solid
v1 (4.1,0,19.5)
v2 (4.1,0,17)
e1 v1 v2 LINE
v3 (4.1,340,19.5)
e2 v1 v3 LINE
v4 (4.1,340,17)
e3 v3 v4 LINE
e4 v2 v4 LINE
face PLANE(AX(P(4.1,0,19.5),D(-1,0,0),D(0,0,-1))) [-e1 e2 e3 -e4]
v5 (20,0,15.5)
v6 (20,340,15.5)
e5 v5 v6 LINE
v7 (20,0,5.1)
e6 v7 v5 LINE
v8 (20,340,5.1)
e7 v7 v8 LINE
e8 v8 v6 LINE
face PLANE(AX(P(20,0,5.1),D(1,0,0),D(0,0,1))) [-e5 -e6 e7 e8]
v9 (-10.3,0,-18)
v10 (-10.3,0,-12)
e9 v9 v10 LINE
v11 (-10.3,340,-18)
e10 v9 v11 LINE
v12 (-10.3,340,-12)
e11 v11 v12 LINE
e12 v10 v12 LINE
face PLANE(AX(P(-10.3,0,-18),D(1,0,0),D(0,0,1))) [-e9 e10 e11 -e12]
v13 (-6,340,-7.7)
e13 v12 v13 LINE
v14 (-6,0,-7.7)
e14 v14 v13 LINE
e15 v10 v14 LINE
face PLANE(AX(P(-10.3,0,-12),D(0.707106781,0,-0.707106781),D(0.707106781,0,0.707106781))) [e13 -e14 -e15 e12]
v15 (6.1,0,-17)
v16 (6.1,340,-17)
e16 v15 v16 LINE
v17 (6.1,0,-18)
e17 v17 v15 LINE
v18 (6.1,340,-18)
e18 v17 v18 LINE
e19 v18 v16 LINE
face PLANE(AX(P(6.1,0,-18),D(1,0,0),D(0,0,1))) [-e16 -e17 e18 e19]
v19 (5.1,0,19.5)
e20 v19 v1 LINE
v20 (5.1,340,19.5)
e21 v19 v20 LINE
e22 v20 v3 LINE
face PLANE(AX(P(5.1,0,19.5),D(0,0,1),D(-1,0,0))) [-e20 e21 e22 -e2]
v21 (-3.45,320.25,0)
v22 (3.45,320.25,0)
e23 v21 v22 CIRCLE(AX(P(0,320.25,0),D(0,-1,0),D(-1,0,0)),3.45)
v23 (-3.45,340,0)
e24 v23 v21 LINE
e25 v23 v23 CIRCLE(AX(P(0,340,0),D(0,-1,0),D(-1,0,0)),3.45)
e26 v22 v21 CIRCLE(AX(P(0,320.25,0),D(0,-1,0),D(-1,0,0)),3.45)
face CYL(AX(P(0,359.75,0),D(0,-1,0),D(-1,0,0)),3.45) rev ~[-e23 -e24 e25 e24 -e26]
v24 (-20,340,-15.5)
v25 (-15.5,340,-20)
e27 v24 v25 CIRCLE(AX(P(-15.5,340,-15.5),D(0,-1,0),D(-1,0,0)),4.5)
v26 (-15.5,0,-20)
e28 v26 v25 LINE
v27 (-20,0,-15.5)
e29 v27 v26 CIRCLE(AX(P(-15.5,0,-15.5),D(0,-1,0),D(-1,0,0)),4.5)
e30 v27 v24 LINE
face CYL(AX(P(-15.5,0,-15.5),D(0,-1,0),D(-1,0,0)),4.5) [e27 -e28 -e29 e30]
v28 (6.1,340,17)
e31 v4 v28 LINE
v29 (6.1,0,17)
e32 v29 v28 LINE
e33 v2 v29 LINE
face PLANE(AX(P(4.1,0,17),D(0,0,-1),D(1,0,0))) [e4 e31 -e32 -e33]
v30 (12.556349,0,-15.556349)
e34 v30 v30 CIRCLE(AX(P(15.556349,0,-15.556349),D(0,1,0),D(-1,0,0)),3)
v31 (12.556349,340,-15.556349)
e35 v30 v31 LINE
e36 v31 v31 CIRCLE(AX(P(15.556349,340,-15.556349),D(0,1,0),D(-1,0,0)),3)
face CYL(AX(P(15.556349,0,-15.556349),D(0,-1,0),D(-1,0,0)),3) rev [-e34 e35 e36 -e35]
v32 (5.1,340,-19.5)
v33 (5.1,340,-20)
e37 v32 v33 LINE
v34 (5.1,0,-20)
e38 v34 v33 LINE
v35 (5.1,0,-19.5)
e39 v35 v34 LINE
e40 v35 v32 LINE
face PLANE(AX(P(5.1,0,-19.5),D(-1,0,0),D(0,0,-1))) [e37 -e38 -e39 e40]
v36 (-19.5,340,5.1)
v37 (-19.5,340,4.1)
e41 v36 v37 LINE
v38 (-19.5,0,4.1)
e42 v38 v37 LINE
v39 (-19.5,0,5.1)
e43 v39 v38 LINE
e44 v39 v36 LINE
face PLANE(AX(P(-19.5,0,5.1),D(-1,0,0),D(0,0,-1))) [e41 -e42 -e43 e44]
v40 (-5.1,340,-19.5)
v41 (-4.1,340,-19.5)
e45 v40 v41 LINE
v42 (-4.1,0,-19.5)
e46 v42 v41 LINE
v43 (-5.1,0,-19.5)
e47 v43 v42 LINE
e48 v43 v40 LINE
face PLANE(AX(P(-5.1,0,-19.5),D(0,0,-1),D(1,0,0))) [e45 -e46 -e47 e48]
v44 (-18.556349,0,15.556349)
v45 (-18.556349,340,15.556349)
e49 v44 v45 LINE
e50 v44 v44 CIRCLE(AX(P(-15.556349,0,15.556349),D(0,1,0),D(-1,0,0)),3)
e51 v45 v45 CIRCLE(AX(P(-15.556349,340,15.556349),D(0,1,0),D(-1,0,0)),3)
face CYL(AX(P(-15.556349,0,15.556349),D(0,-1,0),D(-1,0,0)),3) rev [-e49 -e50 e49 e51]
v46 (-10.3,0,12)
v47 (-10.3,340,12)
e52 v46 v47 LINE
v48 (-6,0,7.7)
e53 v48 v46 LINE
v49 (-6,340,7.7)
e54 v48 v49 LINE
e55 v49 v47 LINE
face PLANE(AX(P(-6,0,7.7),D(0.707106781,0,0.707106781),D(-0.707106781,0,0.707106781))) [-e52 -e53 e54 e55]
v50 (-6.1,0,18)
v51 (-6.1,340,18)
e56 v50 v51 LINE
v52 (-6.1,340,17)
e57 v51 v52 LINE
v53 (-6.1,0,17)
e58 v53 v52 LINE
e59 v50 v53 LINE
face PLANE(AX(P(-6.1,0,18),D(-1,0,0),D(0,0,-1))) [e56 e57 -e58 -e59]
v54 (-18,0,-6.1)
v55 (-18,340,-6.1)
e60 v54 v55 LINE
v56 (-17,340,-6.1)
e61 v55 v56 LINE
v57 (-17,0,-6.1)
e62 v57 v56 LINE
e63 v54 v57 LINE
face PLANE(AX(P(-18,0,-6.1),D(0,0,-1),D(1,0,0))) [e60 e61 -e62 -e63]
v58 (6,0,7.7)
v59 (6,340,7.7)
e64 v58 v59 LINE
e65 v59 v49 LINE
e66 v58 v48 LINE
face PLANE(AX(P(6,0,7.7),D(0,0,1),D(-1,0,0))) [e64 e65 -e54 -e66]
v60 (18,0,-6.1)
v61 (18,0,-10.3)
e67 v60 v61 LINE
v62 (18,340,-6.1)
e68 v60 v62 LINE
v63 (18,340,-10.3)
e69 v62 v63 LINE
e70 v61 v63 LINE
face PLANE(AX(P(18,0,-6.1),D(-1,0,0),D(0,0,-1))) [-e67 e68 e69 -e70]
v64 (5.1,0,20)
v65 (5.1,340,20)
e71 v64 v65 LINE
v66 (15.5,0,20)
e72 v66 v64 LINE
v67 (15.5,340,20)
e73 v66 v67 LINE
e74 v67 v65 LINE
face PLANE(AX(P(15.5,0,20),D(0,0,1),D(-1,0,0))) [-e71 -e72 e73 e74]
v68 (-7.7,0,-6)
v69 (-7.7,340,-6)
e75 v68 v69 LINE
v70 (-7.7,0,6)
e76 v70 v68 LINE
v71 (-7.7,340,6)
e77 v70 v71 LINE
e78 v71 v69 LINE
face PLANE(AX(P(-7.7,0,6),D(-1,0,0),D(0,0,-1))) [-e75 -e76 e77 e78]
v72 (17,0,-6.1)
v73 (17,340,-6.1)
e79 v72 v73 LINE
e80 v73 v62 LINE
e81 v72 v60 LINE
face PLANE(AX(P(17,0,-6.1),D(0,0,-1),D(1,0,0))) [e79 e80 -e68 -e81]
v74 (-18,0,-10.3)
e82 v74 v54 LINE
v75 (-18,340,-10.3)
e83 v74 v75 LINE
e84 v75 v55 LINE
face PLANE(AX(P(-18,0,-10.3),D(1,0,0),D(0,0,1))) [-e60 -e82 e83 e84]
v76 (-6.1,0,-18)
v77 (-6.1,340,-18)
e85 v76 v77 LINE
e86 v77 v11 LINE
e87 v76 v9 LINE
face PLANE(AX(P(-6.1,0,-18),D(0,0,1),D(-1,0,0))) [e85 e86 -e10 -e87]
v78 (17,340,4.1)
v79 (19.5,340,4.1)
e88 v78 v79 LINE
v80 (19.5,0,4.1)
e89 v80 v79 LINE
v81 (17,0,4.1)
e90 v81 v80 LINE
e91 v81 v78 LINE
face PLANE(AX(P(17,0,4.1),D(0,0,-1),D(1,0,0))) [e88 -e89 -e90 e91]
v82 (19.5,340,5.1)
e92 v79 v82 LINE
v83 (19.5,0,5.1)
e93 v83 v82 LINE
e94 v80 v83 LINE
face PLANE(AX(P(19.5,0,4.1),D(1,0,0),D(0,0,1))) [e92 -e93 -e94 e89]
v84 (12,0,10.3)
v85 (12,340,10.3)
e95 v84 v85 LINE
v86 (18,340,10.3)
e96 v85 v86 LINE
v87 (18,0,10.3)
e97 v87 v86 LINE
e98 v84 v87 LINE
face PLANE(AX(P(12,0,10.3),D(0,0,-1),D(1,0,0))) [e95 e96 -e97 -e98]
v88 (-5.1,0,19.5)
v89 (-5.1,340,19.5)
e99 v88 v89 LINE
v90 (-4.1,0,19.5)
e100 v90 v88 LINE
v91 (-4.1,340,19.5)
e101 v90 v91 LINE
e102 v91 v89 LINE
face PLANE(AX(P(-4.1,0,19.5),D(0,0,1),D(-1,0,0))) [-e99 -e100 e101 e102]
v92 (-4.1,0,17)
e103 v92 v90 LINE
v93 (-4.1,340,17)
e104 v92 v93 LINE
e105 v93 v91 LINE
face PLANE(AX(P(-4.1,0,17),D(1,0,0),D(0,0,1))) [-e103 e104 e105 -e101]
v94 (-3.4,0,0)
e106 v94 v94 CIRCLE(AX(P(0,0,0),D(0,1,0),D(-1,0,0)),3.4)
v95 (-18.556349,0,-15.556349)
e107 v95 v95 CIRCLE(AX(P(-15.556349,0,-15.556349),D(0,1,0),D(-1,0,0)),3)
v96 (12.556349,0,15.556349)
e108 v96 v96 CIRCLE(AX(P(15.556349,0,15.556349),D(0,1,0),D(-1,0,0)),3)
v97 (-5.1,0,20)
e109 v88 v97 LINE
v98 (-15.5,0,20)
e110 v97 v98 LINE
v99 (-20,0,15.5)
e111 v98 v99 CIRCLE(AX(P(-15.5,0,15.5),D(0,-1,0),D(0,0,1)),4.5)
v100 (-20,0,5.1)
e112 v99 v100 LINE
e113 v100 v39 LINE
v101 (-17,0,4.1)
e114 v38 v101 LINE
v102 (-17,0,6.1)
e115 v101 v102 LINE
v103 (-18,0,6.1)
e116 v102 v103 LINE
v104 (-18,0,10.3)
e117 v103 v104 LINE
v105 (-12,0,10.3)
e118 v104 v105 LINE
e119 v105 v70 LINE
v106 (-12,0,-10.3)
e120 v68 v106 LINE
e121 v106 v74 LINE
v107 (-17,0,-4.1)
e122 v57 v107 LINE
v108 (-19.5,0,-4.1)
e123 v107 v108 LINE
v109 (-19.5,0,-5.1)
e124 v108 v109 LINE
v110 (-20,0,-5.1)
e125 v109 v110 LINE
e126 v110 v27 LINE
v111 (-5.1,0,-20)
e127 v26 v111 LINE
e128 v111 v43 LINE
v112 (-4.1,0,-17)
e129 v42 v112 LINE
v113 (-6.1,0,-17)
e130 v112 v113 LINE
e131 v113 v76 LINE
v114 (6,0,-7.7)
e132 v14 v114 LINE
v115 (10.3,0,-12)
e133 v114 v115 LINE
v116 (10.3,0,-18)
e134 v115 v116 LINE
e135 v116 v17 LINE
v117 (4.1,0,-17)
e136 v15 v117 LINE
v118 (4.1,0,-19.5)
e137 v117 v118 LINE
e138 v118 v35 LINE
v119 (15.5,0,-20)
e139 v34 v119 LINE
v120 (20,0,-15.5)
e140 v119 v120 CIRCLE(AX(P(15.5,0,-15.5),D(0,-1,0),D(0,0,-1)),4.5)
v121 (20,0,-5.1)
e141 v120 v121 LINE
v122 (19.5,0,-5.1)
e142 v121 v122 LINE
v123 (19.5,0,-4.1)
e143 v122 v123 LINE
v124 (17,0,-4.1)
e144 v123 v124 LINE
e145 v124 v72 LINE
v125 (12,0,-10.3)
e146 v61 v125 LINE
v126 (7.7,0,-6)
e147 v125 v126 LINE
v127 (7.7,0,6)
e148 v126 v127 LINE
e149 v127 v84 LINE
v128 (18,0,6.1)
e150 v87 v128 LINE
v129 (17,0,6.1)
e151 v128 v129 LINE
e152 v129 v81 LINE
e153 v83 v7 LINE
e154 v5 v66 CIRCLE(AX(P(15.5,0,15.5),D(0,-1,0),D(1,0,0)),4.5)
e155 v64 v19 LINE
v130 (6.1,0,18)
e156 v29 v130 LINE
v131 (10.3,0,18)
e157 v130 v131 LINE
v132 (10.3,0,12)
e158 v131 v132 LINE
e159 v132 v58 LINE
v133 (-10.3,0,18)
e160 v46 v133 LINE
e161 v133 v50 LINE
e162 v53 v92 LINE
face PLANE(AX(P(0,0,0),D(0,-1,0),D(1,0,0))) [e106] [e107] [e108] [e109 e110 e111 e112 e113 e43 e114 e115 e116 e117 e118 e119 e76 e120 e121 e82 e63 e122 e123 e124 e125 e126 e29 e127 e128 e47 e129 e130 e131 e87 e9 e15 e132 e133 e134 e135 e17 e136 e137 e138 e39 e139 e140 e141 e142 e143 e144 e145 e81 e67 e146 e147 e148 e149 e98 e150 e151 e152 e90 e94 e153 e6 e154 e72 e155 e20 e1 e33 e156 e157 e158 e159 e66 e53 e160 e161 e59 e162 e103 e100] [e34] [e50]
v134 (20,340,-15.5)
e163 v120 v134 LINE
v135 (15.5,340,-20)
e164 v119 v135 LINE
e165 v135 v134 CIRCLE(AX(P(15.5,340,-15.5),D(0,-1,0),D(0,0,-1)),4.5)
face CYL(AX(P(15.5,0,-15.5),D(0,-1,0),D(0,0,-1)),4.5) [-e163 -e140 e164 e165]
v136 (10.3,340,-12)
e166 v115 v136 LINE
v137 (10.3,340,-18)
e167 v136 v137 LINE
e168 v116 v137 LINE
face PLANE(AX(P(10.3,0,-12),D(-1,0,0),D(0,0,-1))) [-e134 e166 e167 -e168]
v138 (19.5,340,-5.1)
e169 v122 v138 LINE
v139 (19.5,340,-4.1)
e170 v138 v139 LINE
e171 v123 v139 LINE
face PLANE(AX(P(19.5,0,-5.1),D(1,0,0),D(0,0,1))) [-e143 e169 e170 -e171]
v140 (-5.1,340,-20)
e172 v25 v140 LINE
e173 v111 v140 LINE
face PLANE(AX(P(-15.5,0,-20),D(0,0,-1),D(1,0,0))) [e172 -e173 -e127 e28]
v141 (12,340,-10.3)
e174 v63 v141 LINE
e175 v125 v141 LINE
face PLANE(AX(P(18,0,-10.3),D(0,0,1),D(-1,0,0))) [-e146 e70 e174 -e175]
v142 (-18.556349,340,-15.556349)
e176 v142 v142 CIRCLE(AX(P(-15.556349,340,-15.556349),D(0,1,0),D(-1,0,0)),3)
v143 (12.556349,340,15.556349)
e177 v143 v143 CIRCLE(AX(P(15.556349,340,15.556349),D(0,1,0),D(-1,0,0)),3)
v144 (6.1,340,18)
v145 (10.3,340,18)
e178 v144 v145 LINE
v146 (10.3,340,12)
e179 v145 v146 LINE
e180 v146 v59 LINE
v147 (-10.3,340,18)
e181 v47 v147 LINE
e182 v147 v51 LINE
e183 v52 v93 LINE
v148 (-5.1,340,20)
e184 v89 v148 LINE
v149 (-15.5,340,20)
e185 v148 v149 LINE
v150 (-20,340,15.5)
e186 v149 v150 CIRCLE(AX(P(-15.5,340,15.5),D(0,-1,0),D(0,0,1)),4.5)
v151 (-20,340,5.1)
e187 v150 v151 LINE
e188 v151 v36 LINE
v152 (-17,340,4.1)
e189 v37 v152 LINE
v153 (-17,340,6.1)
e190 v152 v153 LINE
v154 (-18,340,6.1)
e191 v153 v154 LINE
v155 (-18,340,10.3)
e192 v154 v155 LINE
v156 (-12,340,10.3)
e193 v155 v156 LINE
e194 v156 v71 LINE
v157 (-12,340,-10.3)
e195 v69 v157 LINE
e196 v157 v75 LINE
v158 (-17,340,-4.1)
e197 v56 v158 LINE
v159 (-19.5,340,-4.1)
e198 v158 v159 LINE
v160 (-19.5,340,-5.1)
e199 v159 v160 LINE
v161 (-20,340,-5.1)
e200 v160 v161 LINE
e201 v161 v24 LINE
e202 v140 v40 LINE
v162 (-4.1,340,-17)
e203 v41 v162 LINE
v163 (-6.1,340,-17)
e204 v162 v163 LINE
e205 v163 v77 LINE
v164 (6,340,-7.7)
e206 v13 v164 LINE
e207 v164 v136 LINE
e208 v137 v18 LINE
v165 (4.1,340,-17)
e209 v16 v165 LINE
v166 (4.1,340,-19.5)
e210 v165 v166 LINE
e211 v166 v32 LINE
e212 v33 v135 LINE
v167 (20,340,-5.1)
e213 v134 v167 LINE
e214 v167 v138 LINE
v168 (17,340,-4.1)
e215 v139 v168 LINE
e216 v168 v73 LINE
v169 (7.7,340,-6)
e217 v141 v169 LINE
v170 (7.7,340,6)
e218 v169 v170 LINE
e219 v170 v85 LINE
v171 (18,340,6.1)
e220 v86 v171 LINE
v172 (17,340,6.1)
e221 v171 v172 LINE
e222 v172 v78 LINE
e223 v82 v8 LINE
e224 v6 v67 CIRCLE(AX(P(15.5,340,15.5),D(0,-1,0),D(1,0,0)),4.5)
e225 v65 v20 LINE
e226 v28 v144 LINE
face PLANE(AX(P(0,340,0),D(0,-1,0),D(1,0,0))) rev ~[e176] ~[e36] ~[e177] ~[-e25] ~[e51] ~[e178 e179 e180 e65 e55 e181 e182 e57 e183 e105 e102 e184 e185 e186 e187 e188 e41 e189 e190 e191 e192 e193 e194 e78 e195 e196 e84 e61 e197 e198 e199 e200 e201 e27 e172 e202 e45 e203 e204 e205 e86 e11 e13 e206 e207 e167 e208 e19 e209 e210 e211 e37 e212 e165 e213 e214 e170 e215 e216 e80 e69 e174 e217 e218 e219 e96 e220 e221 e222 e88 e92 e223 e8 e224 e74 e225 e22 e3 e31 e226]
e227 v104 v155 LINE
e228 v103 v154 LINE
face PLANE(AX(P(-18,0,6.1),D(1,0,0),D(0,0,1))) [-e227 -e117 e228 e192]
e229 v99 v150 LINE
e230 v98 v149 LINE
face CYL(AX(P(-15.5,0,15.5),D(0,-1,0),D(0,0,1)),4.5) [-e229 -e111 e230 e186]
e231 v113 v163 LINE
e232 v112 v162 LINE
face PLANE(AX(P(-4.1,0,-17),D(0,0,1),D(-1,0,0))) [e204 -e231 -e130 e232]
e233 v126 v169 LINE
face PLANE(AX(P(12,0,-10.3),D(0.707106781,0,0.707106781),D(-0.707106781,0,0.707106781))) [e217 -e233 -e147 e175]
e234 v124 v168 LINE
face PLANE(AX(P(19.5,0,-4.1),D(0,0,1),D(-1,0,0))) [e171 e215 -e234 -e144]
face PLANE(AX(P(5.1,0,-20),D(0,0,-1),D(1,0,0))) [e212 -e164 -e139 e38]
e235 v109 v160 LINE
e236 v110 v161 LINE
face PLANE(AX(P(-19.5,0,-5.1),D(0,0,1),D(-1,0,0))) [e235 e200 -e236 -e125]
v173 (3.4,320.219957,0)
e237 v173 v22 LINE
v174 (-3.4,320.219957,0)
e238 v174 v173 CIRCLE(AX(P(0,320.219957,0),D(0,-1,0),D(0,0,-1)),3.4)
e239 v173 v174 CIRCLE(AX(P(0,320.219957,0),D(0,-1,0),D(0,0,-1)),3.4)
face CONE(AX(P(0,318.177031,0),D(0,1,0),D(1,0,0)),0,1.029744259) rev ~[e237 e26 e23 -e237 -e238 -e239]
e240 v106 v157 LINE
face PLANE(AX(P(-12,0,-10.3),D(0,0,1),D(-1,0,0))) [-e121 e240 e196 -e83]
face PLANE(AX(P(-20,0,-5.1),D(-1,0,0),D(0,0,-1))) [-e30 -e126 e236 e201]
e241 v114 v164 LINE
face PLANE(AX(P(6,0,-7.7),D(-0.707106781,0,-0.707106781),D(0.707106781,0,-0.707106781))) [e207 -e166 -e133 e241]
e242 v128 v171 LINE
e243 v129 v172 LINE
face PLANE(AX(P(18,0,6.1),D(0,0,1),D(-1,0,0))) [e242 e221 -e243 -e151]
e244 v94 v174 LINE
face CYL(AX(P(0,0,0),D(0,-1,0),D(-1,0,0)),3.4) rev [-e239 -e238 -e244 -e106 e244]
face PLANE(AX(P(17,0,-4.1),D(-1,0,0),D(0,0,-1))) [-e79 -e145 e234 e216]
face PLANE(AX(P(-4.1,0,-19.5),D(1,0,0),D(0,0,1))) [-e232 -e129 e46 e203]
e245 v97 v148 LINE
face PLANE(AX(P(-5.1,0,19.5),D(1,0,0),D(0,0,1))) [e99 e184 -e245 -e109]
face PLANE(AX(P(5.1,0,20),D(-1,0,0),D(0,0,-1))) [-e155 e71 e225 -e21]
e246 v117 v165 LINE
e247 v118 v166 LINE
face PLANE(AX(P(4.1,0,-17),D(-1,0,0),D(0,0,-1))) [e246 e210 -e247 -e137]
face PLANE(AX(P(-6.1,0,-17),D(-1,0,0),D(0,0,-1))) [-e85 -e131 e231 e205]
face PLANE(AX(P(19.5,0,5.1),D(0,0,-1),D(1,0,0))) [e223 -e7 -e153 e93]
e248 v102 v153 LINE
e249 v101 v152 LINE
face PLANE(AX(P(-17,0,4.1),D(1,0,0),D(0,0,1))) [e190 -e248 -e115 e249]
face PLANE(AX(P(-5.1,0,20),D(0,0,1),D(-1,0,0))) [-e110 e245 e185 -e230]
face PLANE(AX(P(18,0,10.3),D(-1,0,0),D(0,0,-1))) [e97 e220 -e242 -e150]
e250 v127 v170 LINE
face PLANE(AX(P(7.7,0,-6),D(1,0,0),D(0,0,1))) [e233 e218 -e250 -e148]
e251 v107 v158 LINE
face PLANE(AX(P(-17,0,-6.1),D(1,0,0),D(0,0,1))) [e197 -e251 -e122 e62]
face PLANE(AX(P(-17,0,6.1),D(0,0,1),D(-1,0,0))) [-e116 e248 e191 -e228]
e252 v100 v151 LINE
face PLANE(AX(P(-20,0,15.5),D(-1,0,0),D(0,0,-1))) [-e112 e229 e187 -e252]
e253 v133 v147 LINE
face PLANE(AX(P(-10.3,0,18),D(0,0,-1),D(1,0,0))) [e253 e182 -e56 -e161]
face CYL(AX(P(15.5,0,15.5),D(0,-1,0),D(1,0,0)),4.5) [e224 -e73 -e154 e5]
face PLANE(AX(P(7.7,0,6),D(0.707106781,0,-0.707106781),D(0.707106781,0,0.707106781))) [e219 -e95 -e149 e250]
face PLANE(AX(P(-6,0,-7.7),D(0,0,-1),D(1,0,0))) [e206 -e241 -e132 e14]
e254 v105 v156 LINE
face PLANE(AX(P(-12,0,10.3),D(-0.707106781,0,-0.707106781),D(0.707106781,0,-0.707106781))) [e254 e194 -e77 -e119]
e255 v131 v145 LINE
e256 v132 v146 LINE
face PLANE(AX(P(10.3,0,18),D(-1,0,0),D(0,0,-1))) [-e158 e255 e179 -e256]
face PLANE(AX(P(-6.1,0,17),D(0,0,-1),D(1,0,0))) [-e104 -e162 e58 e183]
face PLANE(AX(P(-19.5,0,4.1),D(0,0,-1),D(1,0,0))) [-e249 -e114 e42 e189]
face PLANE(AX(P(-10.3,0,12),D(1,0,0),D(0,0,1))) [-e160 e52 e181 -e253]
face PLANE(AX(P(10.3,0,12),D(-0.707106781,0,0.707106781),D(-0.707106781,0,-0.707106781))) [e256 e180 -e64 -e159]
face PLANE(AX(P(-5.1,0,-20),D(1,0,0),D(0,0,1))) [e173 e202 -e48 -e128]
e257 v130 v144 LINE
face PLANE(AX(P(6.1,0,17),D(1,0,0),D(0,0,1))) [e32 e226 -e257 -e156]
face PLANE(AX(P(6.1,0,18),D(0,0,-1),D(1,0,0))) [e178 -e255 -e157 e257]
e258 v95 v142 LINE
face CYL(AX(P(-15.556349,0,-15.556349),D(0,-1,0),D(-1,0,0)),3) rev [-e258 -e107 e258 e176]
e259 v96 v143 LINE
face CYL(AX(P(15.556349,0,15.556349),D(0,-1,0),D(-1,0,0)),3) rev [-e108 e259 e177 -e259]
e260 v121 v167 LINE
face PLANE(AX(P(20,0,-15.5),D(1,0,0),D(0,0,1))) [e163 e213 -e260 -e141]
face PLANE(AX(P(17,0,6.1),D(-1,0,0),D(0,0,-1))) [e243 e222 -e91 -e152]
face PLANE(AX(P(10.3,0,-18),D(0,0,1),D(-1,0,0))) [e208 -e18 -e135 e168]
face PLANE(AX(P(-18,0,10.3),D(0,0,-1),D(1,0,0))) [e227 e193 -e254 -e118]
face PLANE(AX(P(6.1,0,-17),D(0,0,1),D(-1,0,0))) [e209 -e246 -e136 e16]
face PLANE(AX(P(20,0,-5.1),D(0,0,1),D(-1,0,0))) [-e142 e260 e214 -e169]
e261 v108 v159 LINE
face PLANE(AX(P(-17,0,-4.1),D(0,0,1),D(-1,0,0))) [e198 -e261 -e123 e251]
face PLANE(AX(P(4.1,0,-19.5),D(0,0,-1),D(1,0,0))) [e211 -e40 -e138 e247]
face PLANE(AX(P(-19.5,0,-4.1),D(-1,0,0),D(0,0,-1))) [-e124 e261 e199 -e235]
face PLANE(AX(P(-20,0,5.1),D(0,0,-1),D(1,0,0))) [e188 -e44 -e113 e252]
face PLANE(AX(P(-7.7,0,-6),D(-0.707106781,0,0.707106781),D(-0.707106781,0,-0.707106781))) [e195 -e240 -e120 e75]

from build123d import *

# Parameters (mm, degrees)
SKETCH16_R             = 3.4
SKETCH16_R_2           = 3
MEMBER_1_DEPTH         = 340
HOLE_WIZARD_M8_3_D     = 6.9
HOLE_WIZARD_M8_3_DEPTH = 19.75
HOLE_WIZARD_M8_3_TIP   = 2.072969136


with BuildPart() as part:
    # Sketch16 → Member 1 (new body)
    with BuildSketch(Plane(origin=(0, 0, 0), x_dir=(-1, 0, 0), z_dir=(0, 1, 0))):
        with BuildLine():
            Line((-5.1, 20), (-5.1, 19.5))
            Line((-5.1, 19.5), (-4.1, 19.5))
            Line((-4.1, 19.5), (-4.1, 17))
            Line((-4.1, 17), (-6.1, 17))
            Line((-6.1, 17), (-6.1, 18))
            Line((-6.1, 18), (-10.3, 18))
            Line((-10.3, 18), (-10.3, 12))
            Line((-10.3, 12), (-6, 7.7))
            Line((-6, 7.7), (6, 7.7))
            Line((6, 7.7), (10.3, 12))
            Line((10.3, 12), (10.3, 18))
            Line((10.3, 18), (6.1, 18))
            Line((6.1, 18), (6.1, 17))
            Line((6.1, 17), (4.1, 17))
            Line((4.1, 17), (4.1, 19.5))
            Line((4.1, 19.5), (5.1, 19.5))
            Line((5.1, 19.5), (5.1, 20))
            Line((5.1, 20), (15.5, 20))
            ThreePointArc((15.5, 20), (18.681980515, 18.681980515), (20, 15.5))
            Line((20, 15.5), (20, 5.1))
            Line((20, 5.1), (19.5, 5.1))
            Line((19.5, 5.1), (19.5, 4.1))
            Line((19.5, 4.1), (17, 4.1))
            Line((17, 4.1), (17, 6.1))
            Line((17, 6.1), (18, 6.1))
            Line((18, 6.1), (18, 10.3))
            Line((18, 10.3), (12, 10.3))
            Line((12, 10.3), (7.7, 6))
            Line((7.7, 6), (7.7, -6))
            Line((7.7, -6), (12, -10.3))
            Line((12, -10.3), (18, -10.3))
            Line((18, -10.3), (18, -6.1))
            Line((18, -6.1), (17, -6.1))
            Line((17, -6.1), (17, -4.1))
            Line((17, -4.1), (19.5, -4.1))
            Line((19.5, -4.1), (19.5, -5.1))
            Line((19.5, -5.1), (20, -5.1))
            Line((20, -5.1), (20, -15.5))
            ThreePointArc((20, -15.5), (18.681980515, -18.681980515), (15.5, -20))
            Line((15.5, -20), (5.1, -20))
            Line((5.1, -20), (5.1, -19.5))
            Line((5.1, -19.5), (4.1, -19.5))
            Line((4.1, -19.5), (4.1, -17))
            Line((4.1, -17), (6.1, -17))
            Line((6.1, -17), (6.1, -18))
            Line((6.1, -18), (10.3, -18))
            Line((10.3, -18), (10.3, -12))
            Line((10.3, -12), (6, -7.7))
            Line((6, -7.7), (-6, -7.7))
            Line((-6, -7.7), (-10.3, -12))
            Line((-10.3, -12), (-10.3, -18))
            Line((-10.3, -18), (-6.1, -18))
            Line((-6.1, -18), (-6.1, -17))
            Line((-6.1, -17), (-4.1, -17))
            Line((-4.1, -17), (-4.1, -19.5))
            Line((-4.1, -19.5), (-5.1, -19.5))
            Line((-5.1, -19.5), (-5.1, -20))
            Line((-5.1, -20), (-15.5, -20))
            ThreePointArc((-15.5, -20), (-18.681980515, -18.681980515), (-20, -15.5))
            Line((-20, -15.5), (-20, -5.1))
            Line((-20, -5.1), (-19.5, -5.1))
            Line((-19.5, -5.1), (-19.5, -4.1))
            Line((-19.5, -4.1), (-17, -4.1))
            Line((-17, -4.1), (-17, -6.1))
            Line((-17, -6.1), (-18, -6.1))
            Line((-18, -6.1), (-18, -10.3))
            Line((-18, -10.3), (-12, -10.3))
            Line((-12, -10.3), (-7.7, -6))
            Line((-7.7, -6), (-7.7, 6))
            Line((-7.7, 6), (-12, 10.3))
            Line((-12, 10.3), (-18, 10.3))
            Line((-18, 10.3), (-18, 6.1))
            Line((-18, 6.1), (-17, 6.1))
            Line((-17, 6.1), (-17, 4.1))
            Line((-17, 4.1), (-19.5, 4.1))
            Line((-19.5, 4.1), (-19.5, 5.1))
            Line((-19.5, 5.1), (-20, 5.1))
            Line((-20, 5.1), (-20, 15.5))
            ThreePointArc((-20, 15.5), (-18.681980515, 18.681980515), (-15.5, 20))
            Line((-15.5, 20), (-5.1, 20))
        make_face()
        Circle(SKETCH16_R, mode=Mode.SUBTRACT)
        with Locations((-15.556349186, 15.556349186)):
            Circle(SKETCH16_R_2, mode=Mode.SUBTRACT)
        with Locations((15.556349186, 15.556349186)):
            Circle(SKETCH16_R_2, mode=Mode.SUBTRACT)
        with Locations((15.556349186, -15.556349186)):
            Circle(SKETCH16_R_2, mode=Mode.SUBTRACT)
        with Locations((-15.556349186, -15.556349186)):
            Circle(SKETCH16_R_2, mode=Mode.SUBTRACT)
    extrude(amount=MEMBER_1_DEPTH)

    # M8 螺纹孔3
    with Locations(Plane(origin=(0, 340, 0), x_dir=(1, 0, 0), z_dir=(0, 1, 0))):
        with Locations((0, 0)):
            Hole(HOLE_WIZARD_M8_3_D / 2, depth=HOLE_WIZARD_M8_3_DEPTH)
            with Locations((0, 0, -(HOLE_WIZARD_M8_3_DEPTH + HOLE_WIZARD_M8_3_TIP / 2))):  # 118° drill point
                Cone(0, HOLE_WIZARD_M8_3_D / 2, HOLE_WIZARD_M8_3_TIP, mode=Mode.SUBTRACT)


solid = part.part
